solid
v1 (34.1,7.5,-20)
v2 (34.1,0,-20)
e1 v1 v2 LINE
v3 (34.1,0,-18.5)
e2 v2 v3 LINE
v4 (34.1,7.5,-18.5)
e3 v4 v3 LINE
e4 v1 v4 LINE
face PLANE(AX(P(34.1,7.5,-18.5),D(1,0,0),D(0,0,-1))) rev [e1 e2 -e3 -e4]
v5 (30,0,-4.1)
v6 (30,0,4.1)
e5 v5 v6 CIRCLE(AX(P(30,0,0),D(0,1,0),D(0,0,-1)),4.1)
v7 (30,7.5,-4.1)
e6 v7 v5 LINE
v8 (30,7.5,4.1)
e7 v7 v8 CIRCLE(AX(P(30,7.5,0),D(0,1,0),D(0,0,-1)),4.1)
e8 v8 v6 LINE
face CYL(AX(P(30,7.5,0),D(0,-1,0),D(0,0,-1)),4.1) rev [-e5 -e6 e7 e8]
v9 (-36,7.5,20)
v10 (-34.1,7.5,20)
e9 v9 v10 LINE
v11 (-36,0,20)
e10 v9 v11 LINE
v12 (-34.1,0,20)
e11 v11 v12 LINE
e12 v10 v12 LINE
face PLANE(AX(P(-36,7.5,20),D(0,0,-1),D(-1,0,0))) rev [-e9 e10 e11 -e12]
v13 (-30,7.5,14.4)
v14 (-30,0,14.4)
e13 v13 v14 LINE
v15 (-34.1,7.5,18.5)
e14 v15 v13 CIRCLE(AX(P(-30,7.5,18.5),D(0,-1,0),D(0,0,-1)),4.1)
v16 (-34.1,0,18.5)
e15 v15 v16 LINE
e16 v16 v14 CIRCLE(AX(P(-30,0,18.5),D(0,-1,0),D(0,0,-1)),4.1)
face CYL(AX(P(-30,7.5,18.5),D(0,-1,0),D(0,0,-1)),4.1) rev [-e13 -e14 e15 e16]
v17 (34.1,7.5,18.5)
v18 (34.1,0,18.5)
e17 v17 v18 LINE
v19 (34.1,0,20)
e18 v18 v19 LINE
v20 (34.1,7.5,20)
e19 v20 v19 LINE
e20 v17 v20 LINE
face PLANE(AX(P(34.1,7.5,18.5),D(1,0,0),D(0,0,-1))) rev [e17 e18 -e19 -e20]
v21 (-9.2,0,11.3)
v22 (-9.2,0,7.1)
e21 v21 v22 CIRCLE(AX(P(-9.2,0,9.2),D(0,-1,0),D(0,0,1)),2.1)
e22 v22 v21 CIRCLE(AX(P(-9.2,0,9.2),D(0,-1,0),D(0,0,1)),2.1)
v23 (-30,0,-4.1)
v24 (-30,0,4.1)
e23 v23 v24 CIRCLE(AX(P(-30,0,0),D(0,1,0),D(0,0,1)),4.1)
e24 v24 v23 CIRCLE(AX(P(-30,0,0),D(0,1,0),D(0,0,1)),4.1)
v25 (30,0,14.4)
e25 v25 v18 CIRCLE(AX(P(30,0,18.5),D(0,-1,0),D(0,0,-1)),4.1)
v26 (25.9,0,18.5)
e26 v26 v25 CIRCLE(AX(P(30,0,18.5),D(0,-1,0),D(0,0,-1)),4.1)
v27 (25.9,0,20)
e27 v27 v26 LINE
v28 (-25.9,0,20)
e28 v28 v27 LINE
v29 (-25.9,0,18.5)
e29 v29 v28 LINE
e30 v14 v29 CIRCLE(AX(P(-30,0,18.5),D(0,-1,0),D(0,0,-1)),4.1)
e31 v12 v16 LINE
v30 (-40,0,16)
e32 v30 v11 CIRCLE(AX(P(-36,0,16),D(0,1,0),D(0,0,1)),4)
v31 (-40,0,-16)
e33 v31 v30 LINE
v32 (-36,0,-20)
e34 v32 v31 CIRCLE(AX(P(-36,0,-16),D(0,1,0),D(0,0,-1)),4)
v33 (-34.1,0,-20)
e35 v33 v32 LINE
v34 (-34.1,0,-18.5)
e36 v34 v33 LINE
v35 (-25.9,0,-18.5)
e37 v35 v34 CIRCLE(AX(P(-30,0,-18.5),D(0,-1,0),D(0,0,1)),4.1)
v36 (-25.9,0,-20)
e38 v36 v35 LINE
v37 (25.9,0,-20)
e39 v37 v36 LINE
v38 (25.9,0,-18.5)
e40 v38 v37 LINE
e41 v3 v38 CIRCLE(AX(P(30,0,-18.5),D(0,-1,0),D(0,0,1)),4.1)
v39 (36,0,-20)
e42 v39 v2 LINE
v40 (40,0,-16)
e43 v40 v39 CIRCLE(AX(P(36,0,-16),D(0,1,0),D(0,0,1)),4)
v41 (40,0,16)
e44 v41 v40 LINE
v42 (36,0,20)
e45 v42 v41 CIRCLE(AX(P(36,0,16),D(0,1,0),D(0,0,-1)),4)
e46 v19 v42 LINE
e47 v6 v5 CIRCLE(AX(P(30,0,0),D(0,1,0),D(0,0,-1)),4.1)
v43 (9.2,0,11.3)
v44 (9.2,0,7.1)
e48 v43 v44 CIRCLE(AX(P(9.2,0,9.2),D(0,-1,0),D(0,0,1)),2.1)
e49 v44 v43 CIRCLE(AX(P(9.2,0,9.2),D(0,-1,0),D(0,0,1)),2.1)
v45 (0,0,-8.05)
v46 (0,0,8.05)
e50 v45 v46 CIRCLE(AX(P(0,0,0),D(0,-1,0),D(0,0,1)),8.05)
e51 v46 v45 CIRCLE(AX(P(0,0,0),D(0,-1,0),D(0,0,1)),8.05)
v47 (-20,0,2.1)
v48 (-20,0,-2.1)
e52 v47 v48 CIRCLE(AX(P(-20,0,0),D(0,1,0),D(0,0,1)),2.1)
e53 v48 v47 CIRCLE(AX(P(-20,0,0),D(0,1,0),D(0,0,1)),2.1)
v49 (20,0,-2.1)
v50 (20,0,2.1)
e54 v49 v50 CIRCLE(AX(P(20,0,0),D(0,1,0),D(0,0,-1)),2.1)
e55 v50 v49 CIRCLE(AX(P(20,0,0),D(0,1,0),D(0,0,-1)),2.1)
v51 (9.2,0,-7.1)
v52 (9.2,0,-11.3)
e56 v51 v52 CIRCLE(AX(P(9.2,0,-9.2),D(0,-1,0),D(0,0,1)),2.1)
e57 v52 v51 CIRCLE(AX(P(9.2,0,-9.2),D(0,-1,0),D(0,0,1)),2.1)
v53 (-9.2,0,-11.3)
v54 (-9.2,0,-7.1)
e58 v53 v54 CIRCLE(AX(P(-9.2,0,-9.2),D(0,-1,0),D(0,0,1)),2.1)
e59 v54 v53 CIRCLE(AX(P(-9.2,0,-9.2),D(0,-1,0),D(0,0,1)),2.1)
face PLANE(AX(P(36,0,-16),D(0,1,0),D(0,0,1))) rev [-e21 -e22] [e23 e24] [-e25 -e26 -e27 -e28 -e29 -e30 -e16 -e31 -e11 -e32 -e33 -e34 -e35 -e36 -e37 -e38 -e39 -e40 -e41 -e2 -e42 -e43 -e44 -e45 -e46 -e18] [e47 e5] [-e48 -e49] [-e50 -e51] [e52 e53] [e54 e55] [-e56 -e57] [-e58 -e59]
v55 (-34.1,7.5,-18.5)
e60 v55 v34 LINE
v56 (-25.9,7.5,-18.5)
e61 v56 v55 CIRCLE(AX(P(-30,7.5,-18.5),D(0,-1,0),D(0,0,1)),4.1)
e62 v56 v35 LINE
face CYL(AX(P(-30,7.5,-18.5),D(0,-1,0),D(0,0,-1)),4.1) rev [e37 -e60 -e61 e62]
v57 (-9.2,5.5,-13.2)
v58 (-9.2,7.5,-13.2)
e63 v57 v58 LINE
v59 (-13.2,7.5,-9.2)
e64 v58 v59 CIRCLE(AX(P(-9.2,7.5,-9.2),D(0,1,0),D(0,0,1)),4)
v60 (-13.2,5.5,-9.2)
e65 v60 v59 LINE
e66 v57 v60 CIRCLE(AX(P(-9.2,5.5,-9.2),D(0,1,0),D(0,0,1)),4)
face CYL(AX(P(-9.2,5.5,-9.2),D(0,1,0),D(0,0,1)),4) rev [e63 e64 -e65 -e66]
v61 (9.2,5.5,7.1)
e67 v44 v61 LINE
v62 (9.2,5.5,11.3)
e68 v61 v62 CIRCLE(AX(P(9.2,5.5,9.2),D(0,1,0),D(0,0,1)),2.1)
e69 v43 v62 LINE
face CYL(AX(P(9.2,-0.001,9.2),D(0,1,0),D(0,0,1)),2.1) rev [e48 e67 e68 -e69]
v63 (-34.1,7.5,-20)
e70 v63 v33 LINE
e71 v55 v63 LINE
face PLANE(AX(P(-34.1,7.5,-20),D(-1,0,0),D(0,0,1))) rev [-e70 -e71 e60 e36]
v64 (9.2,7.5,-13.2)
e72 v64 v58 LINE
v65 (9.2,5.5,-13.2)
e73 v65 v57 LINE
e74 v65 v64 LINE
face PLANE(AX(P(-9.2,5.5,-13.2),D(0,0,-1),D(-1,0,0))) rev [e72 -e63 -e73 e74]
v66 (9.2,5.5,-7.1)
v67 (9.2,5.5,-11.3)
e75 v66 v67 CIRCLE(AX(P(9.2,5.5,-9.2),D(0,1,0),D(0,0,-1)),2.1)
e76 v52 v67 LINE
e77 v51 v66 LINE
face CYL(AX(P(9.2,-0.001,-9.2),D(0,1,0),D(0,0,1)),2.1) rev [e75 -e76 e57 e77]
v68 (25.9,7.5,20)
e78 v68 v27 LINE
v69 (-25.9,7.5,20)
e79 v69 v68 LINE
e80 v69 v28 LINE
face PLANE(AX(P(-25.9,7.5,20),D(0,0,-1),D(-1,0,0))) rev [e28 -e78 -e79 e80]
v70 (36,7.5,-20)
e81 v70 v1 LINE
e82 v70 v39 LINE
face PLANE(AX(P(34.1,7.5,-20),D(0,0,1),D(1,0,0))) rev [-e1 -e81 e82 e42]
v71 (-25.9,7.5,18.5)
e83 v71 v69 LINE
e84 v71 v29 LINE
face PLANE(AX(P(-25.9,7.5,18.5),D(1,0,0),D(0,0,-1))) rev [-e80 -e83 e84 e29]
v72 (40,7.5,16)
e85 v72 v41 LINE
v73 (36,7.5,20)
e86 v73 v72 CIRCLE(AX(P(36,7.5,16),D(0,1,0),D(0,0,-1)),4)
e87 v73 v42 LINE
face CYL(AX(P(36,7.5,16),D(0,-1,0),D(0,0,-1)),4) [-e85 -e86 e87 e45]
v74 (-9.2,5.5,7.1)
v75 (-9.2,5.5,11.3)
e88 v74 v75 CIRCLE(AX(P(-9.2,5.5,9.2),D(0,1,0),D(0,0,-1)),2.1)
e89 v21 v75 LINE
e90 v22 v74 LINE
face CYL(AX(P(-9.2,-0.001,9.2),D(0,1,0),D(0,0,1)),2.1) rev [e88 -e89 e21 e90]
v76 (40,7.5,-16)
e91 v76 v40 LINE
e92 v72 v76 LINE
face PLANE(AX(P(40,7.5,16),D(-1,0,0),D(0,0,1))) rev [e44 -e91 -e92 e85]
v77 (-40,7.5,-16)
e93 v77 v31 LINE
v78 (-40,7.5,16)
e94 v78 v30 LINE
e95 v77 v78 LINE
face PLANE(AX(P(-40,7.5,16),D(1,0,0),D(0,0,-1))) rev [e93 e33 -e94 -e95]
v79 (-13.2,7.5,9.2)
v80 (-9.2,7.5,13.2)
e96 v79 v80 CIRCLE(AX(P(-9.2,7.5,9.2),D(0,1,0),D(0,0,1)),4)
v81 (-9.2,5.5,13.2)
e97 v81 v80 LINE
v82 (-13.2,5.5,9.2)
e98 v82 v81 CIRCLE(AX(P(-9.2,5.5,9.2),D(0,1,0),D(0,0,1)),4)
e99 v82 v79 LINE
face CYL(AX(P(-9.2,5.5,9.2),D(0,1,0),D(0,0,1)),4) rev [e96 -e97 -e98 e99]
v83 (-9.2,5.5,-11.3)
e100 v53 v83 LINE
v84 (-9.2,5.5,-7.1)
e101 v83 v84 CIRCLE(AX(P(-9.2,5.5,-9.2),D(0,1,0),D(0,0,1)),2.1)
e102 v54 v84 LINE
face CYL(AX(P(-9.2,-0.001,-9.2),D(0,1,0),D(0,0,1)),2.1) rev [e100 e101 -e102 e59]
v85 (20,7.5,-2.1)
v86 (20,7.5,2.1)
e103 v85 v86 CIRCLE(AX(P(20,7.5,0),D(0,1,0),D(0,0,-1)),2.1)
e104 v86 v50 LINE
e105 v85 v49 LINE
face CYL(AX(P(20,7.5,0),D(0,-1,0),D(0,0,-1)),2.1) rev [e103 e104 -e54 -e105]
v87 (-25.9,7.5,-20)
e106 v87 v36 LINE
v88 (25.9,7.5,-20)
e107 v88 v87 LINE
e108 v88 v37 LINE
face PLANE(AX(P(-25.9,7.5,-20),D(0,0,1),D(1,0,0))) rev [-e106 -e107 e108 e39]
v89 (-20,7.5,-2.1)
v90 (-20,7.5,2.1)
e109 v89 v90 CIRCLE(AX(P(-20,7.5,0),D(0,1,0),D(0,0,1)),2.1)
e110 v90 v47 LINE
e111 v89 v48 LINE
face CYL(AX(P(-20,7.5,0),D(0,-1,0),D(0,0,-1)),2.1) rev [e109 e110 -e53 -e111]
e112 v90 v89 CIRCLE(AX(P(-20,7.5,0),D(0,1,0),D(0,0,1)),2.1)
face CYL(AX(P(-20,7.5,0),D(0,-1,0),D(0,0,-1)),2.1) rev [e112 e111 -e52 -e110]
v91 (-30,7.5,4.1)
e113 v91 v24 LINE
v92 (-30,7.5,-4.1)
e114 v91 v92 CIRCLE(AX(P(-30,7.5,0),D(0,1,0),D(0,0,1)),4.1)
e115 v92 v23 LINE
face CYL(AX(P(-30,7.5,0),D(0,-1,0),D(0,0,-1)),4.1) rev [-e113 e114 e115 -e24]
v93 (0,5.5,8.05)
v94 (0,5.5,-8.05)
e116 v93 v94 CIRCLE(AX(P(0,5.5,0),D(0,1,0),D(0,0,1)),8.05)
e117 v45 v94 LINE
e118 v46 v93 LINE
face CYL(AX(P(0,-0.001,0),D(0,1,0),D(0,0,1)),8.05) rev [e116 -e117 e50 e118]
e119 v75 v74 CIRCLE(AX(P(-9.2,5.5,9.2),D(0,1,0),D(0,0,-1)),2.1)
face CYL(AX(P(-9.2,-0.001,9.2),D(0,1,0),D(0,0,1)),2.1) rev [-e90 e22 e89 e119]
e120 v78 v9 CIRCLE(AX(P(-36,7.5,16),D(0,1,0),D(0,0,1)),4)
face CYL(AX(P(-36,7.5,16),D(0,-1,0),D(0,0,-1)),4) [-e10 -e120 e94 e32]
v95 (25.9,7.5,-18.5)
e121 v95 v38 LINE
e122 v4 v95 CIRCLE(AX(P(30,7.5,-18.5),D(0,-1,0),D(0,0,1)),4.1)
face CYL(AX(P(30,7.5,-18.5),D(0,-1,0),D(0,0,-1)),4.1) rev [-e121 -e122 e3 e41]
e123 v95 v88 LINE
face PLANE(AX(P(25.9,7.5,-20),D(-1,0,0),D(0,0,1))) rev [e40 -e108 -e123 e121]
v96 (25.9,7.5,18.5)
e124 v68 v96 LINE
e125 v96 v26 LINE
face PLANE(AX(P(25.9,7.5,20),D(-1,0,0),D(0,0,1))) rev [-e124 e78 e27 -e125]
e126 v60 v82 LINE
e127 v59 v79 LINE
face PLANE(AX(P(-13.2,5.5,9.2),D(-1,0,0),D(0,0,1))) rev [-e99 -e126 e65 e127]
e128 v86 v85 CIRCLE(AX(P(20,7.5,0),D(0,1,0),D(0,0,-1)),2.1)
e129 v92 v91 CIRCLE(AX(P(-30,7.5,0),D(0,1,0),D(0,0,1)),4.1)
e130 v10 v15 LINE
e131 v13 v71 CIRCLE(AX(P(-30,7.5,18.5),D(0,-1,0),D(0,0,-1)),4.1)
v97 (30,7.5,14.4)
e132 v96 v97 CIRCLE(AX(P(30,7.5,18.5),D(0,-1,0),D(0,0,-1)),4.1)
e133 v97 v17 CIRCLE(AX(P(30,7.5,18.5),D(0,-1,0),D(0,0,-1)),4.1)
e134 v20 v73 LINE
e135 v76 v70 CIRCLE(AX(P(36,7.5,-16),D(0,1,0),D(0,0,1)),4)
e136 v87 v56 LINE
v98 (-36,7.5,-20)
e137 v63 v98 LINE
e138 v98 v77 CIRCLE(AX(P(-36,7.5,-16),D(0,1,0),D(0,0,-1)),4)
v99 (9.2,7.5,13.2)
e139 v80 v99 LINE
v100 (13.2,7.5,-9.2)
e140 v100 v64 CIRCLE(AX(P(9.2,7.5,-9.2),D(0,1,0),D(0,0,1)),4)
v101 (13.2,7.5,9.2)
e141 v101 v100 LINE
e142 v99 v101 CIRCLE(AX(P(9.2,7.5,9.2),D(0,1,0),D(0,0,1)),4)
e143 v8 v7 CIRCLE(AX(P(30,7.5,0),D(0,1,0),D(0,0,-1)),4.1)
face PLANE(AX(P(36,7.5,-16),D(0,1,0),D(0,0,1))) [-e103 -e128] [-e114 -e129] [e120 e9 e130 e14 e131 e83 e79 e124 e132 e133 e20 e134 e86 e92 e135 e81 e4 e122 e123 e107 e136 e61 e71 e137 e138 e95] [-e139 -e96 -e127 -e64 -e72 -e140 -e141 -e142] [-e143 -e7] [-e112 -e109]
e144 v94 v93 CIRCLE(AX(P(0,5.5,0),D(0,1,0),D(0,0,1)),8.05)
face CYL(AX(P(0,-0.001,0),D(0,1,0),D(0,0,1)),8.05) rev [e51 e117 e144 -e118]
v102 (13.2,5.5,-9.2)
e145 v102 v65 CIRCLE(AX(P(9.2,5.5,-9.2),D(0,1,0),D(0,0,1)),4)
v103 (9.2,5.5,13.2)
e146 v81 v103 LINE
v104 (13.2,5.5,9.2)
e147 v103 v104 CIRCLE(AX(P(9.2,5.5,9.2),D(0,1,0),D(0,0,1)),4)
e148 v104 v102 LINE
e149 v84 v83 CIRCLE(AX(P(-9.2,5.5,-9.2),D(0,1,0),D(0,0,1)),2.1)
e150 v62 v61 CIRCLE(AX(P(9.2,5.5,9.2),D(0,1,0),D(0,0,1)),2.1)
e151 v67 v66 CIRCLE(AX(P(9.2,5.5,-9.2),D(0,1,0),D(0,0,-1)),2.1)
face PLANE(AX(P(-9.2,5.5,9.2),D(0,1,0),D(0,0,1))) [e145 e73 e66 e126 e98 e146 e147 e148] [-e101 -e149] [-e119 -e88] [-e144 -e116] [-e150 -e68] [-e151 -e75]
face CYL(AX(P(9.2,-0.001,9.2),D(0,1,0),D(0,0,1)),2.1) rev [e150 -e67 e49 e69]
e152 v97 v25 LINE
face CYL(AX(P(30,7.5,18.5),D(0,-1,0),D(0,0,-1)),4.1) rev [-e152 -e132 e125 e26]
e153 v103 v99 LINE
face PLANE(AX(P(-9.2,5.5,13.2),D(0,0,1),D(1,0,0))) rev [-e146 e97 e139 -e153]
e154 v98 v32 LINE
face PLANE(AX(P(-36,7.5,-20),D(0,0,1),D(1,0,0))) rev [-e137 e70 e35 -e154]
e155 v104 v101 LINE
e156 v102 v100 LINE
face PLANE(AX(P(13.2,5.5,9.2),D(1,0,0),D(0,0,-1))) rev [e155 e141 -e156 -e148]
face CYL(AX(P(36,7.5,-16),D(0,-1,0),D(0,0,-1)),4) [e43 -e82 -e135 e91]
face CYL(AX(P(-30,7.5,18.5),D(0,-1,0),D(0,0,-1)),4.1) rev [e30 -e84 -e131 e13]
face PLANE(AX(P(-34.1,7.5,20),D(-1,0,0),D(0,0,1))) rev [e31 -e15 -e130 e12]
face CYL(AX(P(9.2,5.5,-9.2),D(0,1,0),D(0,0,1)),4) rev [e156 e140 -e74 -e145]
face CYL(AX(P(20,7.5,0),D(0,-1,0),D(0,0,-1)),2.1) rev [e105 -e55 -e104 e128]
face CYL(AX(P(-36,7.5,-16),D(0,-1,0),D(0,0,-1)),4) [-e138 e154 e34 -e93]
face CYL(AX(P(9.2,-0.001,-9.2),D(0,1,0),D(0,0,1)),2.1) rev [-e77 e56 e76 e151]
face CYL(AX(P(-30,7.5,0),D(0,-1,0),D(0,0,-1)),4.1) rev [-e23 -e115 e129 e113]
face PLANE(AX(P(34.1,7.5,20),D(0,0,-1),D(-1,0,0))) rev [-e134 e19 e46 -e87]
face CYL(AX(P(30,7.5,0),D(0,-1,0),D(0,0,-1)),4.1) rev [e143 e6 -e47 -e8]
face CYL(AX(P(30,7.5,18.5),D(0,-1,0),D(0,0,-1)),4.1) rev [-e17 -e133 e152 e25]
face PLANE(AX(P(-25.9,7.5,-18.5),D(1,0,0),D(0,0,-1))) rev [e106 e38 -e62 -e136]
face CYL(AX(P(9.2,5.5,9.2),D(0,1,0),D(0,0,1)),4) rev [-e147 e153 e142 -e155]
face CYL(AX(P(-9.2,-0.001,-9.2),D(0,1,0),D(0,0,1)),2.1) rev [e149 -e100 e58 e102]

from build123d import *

# Parameters (mm, degrees)
BASE_PLATE_PROFILE_SKETCH_R               = 4.1
BASE_PLATE_PROFILE_SKETCH_R_2             = 2.1
BASE_PLATE_7_5MM_DEPTH                    = 7.5
CONNECTOR_RECESS_26_4MM_X_2MM_DEPTH       = 2
CONNECTOR_BORE_AND_SCREW_HOLES_REACH      = 47.058
CONNECTOR_BORE_AND_SCREW_HOLES_SKETCH_R   = 8.05
CONNECTOR_BORE_AND_SCREW_HOLES_SKETCH_R_2 = 2.1


with BuildPart() as part:
    # Base Plate Profile Sketch → Base Plate 7.5mm (new body)
    with BuildSketch(Plane(origin=(0, 0, 0), x_dir=(1, 0, 0), z_dir=(0, 1, 0))):
        with BuildLine():
            Line((-34.1, 20), (-34.1, 18.5))
            ThreePointArc((-34.1, 18.5), (-30, 14.4), (-25.9, 18.5))
            Line((-25.9, 18.5), (-25.9, 20))
            Line((-25.9, 20), (25.9, 20))
            Line((25.9, 20), (25.9, 18.5))
            ThreePointArc((25.9, 18.5), (30, 14.4), (34.1, 18.5))
            Line((34.1, 18.5), (34.1, 20))
            Line((34.1, 20), (36, 20))
            ThreePointArc((36, 20), (38.828427125, 18.828427125), (40, 16))
            Line((40, 16), (40, -16))
            ThreePointArc((40, -16), (38.828427125, -18.828427125), (36, -20))
            Line((36, -20), (34.1, -20))
            Line((34.1, -20), (34.1, -18.5))
            ThreePointArc((34.1, -18.5), (30, -14.4), (25.9, -18.5))
            Line((25.9, -18.5), (25.9, -20))
            Line((25.9, -20), (-25.9, -20))
            Line((-25.9, -20), (-25.9, -18.5))
            ThreePointArc((-25.9, -18.5), (-30, -14.4), (-34.1, -18.5))
            Line((-34.1, -18.5), (-34.1, -20))
            Line((-34.1, -20), (-36, -20))
            ThreePointArc((-36, -20), (-38.828427125, -18.828427125), (-40, -16))
            Line((-40, -16), (-40, 16))
            ThreePointArc((-40, 16), (-38.828427125, 18.828427125), (-36, 20))
            Line((-36, 20), (-34.1, 20))
        make_face()
        with Locations(Location((-30, 0, 0), (0, 0, 270))):
            Circle(BASE_PLATE_PROFILE_SKETCH_R, mode=Mode.SUBTRACT)
        with Locations(Location((30, 0, 0), (0, 0, 90))):
            Circle(BASE_PLATE_PROFILE_SKETCH_R, mode=Mode.SUBTRACT)
        with Locations(Location((-20, 0, 0), (0, 0, 270))):
            Circle(BASE_PLATE_PROFILE_SKETCH_R_2, mode=Mode.SUBTRACT)
        with Locations(Location((20, 0, 0), (0, 0, 90))):
            Circle(BASE_PLATE_PROFILE_SKETCH_R_2, mode=Mode.SUBTRACT)
    extrude(amount=BASE_PLATE_7_5MM_DEPTH)

    # Connector Recess Sketch → Connector Recess 26.4mm x 2mm (cut)
    with BuildSketch(Plane(origin=(0, 7.5, 0), x_dir=(1, 0, 0), z_dir=(0, 1, 0))):
        with BuildLine():
            Line((-9.2, -13.2), (9.2, -13.2))
            ThreePointArc((9.2, -13.2), (12.028427125, -12.028427125), (13.2, -9.2))
            Line((13.2, -9.2), (13.2, 9.2))
            ThreePointArc((13.2, 9.2), (12.028427125, 12.028427125), (9.2, 13.2))
            Line((9.2, 13.2), (-9.2, 13.2))
            ThreePointArc((-9.2, 13.2), (-12.028427125, 12.028427125), (-13.2, 9.2))
            Line((-13.2, 9.2), (-13.2, -9.2))
            ThreePointArc((-13.2, -9.2), (-12.028427125, -12.028427125), (-9.2, -13.2))
        make_face()
    extrude(amount=-CONNECTOR_RECESS_26_4MM_X_2MM_DEPTH, mode=Mode.SUBTRACT)

    # Connector Bore and Screw Holes Sketch → Connector Bore and Screw Holes (cut, up to next)
    with BuildSketch(Plane(origin=(0, 5.5, 0), x_dir=(1, 0, 0), z_dir=(0, 1, 0)), mode=Mode.PRIVATE) as connector_bore_and_screw_holes_sk1:
        with Locations(Location((0, 0, 0), (0, 0, 270))):
            Circle(CONNECTOR_BORE_AND_SCREW_HOLES_SKETCH_R)
    connector_bore_and_screw_holes_tool1 = extrude(connector_bore_and_screw_holes_sk1.sketch, amount=-CONNECTOR_BORE_AND_SCREW_HOLES_REACH, mode=Mode.PRIVATE) & part.part
    # Connector Bore and Screw Holes Sketch → Connector Bore and Screw Holes (cut, up to next)
    with BuildSketch(Plane(origin=(0, 5.5, 0), x_dir=(1, 0, 0), z_dir=(0, 1, 0)), mode=Mode.PRIVATE) as connector_bore_and_screw_holes_sk2:
        with Locations(Location((-9.2, 9.2, 0), (0, 0, 270))):
            Circle(CONNECTOR_BORE_AND_SCREW_HOLES_SKETCH_R_2)
    connector_bore_and_screw_holes_tool2 = extrude(connector_bore_and_screw_holes_sk2.sketch, amount=-CONNECTOR_BORE_AND_SCREW_HOLES_REACH, mode=Mode.PRIVATE) & part.part
    # Connector Bore and Screw Holes Sketch → Connector Bore and Screw Holes (cut, up to next)
    with BuildSketch(Plane(origin=(0, 5.5, 0), x_dir=(1, 0, 0), z_dir=(0, 1, 0)), mode=Mode.PRIVATE) as connector_bore_and_screw_holes_sk3:
        with Locations(Location((-9.2, -9.2, 0), (0, 0, 270))):
            Circle(CONNECTOR_BORE_AND_SCREW_HOLES_SKETCH_R_2)
    connector_bore_and_screw_holes_tool3 = extrude(connector_bore_and_screw_holes_sk3.sketch, amount=-CONNECTOR_BORE_AND_SCREW_HOLES_REACH, mode=Mode.PRIVATE) & part.part
    # Connector Bore and Screw Holes Sketch → Connector Bore and Screw Holes (cut, up to next)
    with BuildSketch(Plane(origin=(0, 5.5, 0), x_dir=(1, 0, 0), z_dir=(0, 1, 0)), mode=Mode.PRIVATE) as connector_bore_and_screw_holes_sk4:
        with Locations(Location((9.2, -9.2, 0), (0, 0, 270))):
            Circle(CONNECTOR_BORE_AND_SCREW_HOLES_SKETCH_R_2)
    connector_bore_and_screw_holes_tool4 = extrude(connector_bore_and_screw_holes_sk4.sketch, amount=-CONNECTOR_BORE_AND_SCREW_HOLES_REACH, mode=Mode.PRIVATE) & part.part
    # Connector Bore and Screw Holes Sketch → Connector Bore and Screw Holes (cut, up to next)
    with BuildSketch(Plane(origin=(0, 5.5, 0), x_dir=(1, 0, 0), z_dir=(0, 1, 0)), mode=Mode.PRIVATE) as connector_bore_and_screw_holes_sk5:
        with Locations(Location((9.2, 9.2, 0), (0, 0, 270))):
            Circle(CONNECTOR_BORE_AND_SCREW_HOLES_SKETCH_R_2)
    connector_bore_and_screw_holes_tool5 = extrude(connector_bore_and_screw_holes_sk5.sketch, amount=-CONNECTOR_BORE_AND_SCREW_HOLES_REACH, mode=Mode.PRIVATE) & part.part
    add(connector_bore_and_screw_holes_tool1.solids().sort_by_distance((0, 5.5, 0))[0], mode=Mode.SUBTRACT)
    add(connector_bore_and_screw_holes_tool2.solids().sort_by_distance((-9.2, 5.5, -9.2))[0], mode=Mode.SUBTRACT)
    add(connector_bore_and_screw_holes_tool3.solids().sort_by_distance((-9.2, 5.5, 9.2))[0], mode=Mode.SUBTRACT)
    add(connector_bore_and_screw_holes_tool4.solids().sort_by_distance((9.2, 5.5, 9.2))[0], mode=Mode.SUBTRACT)
    add(connector_bore_and_screw_holes_tool5.solids().sort_by_distance((9.2, 5.5, -9.2))[0], mode=Mode.SUBTRACT)


solid = part.part
